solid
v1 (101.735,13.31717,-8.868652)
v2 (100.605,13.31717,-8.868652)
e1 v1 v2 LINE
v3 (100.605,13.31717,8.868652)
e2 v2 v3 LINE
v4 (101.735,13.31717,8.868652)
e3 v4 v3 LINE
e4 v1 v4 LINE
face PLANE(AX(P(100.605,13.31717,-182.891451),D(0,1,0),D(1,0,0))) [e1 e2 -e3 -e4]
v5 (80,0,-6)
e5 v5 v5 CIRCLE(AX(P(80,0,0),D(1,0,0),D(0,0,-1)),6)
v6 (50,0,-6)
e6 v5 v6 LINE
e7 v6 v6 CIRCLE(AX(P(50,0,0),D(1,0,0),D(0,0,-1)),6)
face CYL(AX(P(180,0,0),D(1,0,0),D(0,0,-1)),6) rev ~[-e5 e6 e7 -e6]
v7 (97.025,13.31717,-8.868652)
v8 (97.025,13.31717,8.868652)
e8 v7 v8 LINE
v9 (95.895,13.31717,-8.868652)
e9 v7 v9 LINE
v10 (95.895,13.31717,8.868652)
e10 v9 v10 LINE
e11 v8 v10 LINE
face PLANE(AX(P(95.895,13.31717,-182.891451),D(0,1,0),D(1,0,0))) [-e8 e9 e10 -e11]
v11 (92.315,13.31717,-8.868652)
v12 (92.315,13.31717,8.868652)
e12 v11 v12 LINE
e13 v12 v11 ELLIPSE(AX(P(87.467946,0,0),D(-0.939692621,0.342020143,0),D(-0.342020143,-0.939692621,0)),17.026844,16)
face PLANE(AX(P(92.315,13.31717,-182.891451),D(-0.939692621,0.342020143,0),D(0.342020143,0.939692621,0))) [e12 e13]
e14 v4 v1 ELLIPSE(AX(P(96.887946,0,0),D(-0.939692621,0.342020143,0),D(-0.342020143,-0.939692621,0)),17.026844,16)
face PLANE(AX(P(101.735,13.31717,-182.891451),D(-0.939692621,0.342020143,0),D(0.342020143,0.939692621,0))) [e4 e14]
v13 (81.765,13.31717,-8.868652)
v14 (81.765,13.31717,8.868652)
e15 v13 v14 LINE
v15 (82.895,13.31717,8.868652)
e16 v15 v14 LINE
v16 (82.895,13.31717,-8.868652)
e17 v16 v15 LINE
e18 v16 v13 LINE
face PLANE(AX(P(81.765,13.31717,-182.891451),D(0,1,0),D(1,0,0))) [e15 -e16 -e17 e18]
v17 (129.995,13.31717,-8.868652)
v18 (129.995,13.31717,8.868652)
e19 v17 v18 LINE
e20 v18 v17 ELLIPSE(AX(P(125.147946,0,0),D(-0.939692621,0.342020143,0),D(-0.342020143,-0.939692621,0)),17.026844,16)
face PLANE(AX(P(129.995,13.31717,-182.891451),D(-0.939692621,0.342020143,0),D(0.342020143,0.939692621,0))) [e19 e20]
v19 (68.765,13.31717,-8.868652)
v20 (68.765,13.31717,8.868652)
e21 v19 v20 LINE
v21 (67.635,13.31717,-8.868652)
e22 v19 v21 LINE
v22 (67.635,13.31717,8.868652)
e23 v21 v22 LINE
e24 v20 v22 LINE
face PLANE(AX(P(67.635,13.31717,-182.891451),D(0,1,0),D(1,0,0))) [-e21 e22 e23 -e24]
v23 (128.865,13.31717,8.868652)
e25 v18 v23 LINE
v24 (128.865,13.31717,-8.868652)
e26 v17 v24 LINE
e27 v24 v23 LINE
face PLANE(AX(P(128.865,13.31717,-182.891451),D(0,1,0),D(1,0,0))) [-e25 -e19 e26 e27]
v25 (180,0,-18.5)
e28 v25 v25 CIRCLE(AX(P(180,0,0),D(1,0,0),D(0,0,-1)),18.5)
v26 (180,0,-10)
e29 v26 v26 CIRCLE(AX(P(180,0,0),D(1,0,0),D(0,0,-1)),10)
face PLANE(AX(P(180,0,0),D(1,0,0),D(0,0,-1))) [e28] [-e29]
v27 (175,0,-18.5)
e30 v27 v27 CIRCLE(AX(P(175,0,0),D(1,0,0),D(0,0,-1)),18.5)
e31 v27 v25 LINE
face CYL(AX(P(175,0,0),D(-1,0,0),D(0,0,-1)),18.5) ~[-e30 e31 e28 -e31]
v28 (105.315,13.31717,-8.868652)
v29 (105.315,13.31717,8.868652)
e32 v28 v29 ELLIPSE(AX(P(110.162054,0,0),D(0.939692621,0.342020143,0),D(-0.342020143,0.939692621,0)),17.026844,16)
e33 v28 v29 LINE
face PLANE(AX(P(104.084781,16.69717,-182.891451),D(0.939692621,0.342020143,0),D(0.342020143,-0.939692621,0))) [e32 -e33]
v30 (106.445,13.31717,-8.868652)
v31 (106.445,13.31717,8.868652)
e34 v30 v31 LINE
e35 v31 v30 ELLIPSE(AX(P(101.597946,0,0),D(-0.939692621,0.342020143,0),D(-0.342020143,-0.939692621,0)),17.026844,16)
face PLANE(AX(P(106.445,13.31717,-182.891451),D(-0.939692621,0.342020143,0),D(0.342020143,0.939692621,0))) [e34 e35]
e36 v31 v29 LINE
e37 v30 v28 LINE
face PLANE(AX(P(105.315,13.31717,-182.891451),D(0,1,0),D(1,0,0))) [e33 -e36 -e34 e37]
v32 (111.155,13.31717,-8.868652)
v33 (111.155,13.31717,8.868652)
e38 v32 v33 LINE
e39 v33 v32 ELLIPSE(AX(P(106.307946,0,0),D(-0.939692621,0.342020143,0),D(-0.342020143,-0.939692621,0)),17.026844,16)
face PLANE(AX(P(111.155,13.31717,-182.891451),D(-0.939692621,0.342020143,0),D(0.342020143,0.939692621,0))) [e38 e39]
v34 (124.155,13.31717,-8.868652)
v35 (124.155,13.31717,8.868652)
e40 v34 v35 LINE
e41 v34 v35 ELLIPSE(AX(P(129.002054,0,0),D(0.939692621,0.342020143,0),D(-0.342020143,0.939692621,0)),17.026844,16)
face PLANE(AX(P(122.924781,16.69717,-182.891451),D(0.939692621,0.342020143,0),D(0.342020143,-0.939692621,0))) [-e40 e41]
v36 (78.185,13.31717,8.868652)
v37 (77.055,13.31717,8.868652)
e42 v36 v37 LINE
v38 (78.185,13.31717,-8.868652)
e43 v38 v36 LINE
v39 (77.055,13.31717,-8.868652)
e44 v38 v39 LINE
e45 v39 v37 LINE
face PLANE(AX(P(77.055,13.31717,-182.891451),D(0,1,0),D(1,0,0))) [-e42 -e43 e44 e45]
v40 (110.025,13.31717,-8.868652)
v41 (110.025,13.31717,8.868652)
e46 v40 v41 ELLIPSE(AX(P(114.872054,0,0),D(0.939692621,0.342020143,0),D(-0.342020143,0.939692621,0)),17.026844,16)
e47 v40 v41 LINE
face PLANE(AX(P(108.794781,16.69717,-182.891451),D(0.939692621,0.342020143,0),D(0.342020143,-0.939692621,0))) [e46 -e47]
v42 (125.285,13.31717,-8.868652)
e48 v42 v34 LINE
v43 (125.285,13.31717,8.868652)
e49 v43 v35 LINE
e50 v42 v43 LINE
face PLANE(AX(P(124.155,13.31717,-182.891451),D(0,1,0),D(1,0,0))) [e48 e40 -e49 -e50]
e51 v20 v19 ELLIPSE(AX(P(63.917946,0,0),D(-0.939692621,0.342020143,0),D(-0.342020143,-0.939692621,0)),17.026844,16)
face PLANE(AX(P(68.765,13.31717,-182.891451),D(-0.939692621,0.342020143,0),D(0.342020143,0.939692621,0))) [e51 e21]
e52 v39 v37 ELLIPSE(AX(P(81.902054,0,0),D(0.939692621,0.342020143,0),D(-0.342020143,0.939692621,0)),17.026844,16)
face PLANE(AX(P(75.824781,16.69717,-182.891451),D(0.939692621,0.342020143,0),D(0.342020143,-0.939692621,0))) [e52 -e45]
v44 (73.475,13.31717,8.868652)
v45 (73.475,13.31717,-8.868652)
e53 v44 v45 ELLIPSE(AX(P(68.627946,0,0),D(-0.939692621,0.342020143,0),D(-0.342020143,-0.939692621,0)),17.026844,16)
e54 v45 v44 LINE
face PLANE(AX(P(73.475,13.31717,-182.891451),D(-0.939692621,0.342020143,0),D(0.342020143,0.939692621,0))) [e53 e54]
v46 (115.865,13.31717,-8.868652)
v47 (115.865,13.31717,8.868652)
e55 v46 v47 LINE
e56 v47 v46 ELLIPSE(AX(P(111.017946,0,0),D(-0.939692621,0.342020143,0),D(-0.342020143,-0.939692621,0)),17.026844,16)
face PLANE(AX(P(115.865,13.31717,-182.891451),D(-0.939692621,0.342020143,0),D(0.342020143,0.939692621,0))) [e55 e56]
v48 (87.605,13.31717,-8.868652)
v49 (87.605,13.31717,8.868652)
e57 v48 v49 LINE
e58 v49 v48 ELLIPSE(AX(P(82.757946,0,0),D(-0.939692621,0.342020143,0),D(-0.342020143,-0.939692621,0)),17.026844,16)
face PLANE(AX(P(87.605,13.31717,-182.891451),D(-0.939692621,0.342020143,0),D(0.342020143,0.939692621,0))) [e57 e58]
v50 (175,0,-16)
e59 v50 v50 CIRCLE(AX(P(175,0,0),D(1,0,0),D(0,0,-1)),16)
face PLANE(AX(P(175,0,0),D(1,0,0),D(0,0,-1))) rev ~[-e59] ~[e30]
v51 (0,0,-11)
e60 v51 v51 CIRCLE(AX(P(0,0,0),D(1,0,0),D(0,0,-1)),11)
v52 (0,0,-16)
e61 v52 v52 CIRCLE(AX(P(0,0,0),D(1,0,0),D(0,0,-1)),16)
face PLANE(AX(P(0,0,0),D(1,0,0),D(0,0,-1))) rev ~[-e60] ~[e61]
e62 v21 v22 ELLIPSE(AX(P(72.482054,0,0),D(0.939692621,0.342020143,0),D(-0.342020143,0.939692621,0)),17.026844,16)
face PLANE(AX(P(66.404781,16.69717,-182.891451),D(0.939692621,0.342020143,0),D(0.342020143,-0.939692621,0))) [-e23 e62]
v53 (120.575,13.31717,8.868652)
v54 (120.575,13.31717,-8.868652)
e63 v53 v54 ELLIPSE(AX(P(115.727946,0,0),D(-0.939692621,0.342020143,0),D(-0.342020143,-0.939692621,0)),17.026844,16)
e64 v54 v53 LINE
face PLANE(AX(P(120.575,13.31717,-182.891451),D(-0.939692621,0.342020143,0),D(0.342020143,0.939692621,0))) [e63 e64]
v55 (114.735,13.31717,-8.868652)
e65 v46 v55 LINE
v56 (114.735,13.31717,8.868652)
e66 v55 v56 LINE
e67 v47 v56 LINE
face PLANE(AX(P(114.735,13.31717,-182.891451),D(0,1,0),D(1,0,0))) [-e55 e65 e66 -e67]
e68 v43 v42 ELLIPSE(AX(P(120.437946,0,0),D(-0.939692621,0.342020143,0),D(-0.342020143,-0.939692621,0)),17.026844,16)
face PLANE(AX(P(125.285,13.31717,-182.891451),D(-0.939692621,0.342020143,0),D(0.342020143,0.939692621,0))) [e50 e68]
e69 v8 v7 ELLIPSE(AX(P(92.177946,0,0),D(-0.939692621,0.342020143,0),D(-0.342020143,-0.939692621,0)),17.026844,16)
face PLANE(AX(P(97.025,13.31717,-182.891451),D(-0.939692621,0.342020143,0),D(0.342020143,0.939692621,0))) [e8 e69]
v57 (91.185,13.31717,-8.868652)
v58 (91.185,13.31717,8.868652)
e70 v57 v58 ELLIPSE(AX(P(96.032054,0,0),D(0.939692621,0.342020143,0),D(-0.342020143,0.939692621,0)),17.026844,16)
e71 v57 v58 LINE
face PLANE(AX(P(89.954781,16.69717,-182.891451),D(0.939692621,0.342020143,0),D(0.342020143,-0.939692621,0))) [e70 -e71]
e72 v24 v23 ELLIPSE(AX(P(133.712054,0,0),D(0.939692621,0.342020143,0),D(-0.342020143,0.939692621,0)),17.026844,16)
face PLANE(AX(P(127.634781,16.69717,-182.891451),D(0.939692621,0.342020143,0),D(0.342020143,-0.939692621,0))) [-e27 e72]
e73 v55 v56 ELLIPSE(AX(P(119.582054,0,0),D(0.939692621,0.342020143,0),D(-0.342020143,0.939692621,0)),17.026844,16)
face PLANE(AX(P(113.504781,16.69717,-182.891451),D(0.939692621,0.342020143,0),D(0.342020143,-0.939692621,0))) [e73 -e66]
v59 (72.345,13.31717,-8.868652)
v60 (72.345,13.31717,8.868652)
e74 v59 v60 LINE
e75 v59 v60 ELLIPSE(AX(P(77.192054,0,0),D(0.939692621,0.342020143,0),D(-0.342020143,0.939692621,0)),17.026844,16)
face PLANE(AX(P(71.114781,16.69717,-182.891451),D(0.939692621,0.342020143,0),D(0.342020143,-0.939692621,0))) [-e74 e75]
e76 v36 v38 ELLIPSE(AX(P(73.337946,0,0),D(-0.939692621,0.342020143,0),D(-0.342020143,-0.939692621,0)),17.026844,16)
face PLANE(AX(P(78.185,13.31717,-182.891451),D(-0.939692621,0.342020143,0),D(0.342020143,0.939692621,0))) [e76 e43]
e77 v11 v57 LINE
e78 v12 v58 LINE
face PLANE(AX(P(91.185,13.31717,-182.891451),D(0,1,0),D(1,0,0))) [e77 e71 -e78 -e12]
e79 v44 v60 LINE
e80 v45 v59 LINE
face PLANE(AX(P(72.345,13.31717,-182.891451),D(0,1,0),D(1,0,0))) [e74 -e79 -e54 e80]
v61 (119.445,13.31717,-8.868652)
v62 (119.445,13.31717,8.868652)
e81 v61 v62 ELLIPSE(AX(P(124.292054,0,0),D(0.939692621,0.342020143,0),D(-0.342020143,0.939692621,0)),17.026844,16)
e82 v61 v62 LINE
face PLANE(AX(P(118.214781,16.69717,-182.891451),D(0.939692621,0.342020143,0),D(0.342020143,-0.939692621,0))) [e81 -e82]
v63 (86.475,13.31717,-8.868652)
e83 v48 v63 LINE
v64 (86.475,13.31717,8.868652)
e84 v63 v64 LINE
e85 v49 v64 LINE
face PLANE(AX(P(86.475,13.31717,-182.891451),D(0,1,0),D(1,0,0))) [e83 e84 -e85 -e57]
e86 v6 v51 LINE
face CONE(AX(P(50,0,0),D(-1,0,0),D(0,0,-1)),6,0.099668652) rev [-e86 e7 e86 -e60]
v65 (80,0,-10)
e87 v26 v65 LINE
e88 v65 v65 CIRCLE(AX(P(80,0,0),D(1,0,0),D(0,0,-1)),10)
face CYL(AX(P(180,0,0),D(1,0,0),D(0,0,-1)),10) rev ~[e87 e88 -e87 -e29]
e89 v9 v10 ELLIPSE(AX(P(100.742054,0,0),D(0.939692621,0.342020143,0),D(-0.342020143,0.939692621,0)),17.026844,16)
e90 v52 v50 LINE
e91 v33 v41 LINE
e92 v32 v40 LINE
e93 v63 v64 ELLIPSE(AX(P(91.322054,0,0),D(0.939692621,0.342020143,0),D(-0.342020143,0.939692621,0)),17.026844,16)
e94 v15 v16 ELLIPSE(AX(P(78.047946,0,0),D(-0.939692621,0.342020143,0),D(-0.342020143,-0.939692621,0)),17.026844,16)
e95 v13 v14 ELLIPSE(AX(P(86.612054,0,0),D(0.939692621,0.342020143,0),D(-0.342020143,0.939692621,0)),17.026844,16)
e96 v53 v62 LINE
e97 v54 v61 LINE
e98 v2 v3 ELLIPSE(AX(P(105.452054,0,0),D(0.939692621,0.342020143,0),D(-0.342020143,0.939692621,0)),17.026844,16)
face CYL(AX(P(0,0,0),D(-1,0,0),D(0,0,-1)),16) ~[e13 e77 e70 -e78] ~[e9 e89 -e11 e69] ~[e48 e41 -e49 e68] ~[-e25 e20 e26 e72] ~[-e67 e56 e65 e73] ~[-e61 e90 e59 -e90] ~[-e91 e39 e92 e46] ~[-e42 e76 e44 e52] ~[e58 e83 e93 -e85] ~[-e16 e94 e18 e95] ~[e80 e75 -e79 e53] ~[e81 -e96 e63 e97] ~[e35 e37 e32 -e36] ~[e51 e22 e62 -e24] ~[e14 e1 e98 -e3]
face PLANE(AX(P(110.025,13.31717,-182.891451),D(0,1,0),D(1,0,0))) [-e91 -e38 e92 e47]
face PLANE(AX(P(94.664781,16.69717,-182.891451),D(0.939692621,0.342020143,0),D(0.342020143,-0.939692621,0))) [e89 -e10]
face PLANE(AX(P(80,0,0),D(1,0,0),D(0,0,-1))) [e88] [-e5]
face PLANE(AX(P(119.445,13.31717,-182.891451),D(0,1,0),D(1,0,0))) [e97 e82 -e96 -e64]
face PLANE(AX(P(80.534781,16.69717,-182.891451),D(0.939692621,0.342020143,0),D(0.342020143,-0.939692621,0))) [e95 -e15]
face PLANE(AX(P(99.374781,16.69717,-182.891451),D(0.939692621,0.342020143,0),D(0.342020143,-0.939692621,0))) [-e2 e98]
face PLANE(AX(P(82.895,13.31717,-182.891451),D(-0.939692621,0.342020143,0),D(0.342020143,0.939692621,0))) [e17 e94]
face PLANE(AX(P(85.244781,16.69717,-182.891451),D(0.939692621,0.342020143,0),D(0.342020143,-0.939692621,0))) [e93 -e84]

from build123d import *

# Parameters (mm, degrees)
SKETCH1_R               = 16
BOSS_EXTRUDE1_DEPTH     = 175
SKETCH2_R               = 18.5
BOSS_EXTRUDE2_DEPTH     = 5
SKETCH3_R               = 10
CUT_EXTRUDE1_DEPTH      = 100
SKETCH4_R               = 6
CUT_EXTRUDE2_DEPTH      = 8000
CUT_EXTRUDE3_DEPTH      = 182.891451146
CUT_EXTRUDE3_DEPTH_BACK = 182.891451146


with BuildPart() as part:
    # Sketch1 → Boss-Extrude1 (new body)
    with BuildSketch(Plane(origin=(0, 0, 0), x_dir=(0, 0, -1), z_dir=(1, 0, 0))):
        Circle(SKETCH1_R)
    extrude(amount=BOSS_EXTRUDE1_DEPTH)

    # Sketch2 → Boss-Extrude2 (add)
    with BuildSketch(Plane(origin=(175, 0, 0), x_dir=(0, 0, -1), z_dir=(1, 0, 0))):
        Circle(SKETCH2_R)
    extrude(amount=BOSS_EXTRUDE2_DEPTH)

    # Sketch3 → Cut-Extrude1 (cut)
    with BuildSketch(Plane(origin=(180, 0, 0), x_dir=(0, 0, -1), z_dir=(1, 0, 0))):
        Circle(SKETCH3_R)
    extrude(amount=-CUT_EXTRUDE1_DEPTH, mode=Mode.SUBTRACT)

    # Sketch4 → Cut-Extrude2 (cut)
    with BuildSketch(Plane(origin=(180, 0, 0), x_dir=(0, 0, -1), z_dir=(1, 0, 0))):
        Circle(SKETCH4_R)
    extrude(amount=-CUT_EXTRUDE2_DEPTH, mode=Mode.SUBTRACT)

    # Sketch5 → Cut-Revolve1 (revolve, cut)
    with BuildSketch(Plane.XY, mode=Mode.PRIVATE) as cut_revolve1_sk:
        Polygon((0, 0), (50, 0), (50, 6), (0, 11), align=None)
    revolve(cut_revolve1_sk.sketch.rotate(Axis((0, 0, 0), (1, 0, 0)), 270), axis=Axis((0, 0, 0), (1, 0, 0)), mode=Mode.SUBTRACT)

    # Sketch6 → Cut-Extrude3 (cut, two sides: drawn at the far end of the back side and taken through both)
    with BuildSketch(Plane.XY.offset(-CUT_EXTRUDE3_DEPTH_BACK)):
        Polygon((69.995219392, 16.697170081), (66.404780608, 16.697170081), (67.635, 13.317170081), (68.765, 13.317170081), align=None)
        Polygon((72.345, 13.317170081), (73.475, 13.317170081), (74.705219392, 16.697170081), (71.114780608, 16.697170081), align=None)
        Polygon((77.055, 13.317170081), (78.185, 13.317170081), (79.415219392, 16.697170081), (75.824780608, 16.697170081), align=None)
        Polygon((81.765, 13.317170081), (82.895, 13.317170081), (84.125219392, 16.697170081), (80.534780608, 16.697170081), align=None)
        Polygon((86.475, 13.317170081), (87.605, 13.317170081), (88.835219392, 16.697170081), (85.244780608, 16.697170081), align=None)
        Polygon((91.185, 13.317170081), (92.315, 13.317170081), (93.545219392, 16.697170081), (89.954780608, 16.697170081), align=None)
        Polygon((95.895, 13.317170081), (97.025, 13.317170081), (98.255219392, 16.697170081), (94.664780608, 16.697170081), align=None)
        Polygon((100.605, 13.317170081), (101.735, 13.317170081), (102.965219392, 16.697170081), (99.374780608, 16.697170081), align=None)
        Polygon((105.315, 13.317170081), (106.445, 13.317170081), (107.675219392, 16.697170081), (104.084780608, 16.697170081), align=None)
        Polygon((110.025, 13.317170081), (111.155, 13.317170081), (112.385219392, 16.697170081), (108.794780608, 16.697170081), align=None)
        Polygon((114.735, 13.317170081), (115.865, 13.317170081), (117.095219392, 16.697170081), (113.504780608, 16.697170081), align=None)
        Polygon((119.445, 13.317170081), (120.575, 13.317170081), (121.805219392, 16.697170081), (118.214780608, 16.697170081), align=None)
        Polygon((124.155, 13.317170081), (125.285, 13.317170081), (126.515219392, 16.697170081), (122.924780608, 16.697170081), align=None)
        Polygon((128.865, 13.317170081), (129.995, 13.317170081), (131.225219392, 16.697170081), (127.634780608, 16.697170081), align=None)
    extrude(amount=CUT_EXTRUDE3_DEPTH + CUT_EXTRUDE3_DEPTH_BACK, mode=Mode.SUBTRACT)


solid = part.part
